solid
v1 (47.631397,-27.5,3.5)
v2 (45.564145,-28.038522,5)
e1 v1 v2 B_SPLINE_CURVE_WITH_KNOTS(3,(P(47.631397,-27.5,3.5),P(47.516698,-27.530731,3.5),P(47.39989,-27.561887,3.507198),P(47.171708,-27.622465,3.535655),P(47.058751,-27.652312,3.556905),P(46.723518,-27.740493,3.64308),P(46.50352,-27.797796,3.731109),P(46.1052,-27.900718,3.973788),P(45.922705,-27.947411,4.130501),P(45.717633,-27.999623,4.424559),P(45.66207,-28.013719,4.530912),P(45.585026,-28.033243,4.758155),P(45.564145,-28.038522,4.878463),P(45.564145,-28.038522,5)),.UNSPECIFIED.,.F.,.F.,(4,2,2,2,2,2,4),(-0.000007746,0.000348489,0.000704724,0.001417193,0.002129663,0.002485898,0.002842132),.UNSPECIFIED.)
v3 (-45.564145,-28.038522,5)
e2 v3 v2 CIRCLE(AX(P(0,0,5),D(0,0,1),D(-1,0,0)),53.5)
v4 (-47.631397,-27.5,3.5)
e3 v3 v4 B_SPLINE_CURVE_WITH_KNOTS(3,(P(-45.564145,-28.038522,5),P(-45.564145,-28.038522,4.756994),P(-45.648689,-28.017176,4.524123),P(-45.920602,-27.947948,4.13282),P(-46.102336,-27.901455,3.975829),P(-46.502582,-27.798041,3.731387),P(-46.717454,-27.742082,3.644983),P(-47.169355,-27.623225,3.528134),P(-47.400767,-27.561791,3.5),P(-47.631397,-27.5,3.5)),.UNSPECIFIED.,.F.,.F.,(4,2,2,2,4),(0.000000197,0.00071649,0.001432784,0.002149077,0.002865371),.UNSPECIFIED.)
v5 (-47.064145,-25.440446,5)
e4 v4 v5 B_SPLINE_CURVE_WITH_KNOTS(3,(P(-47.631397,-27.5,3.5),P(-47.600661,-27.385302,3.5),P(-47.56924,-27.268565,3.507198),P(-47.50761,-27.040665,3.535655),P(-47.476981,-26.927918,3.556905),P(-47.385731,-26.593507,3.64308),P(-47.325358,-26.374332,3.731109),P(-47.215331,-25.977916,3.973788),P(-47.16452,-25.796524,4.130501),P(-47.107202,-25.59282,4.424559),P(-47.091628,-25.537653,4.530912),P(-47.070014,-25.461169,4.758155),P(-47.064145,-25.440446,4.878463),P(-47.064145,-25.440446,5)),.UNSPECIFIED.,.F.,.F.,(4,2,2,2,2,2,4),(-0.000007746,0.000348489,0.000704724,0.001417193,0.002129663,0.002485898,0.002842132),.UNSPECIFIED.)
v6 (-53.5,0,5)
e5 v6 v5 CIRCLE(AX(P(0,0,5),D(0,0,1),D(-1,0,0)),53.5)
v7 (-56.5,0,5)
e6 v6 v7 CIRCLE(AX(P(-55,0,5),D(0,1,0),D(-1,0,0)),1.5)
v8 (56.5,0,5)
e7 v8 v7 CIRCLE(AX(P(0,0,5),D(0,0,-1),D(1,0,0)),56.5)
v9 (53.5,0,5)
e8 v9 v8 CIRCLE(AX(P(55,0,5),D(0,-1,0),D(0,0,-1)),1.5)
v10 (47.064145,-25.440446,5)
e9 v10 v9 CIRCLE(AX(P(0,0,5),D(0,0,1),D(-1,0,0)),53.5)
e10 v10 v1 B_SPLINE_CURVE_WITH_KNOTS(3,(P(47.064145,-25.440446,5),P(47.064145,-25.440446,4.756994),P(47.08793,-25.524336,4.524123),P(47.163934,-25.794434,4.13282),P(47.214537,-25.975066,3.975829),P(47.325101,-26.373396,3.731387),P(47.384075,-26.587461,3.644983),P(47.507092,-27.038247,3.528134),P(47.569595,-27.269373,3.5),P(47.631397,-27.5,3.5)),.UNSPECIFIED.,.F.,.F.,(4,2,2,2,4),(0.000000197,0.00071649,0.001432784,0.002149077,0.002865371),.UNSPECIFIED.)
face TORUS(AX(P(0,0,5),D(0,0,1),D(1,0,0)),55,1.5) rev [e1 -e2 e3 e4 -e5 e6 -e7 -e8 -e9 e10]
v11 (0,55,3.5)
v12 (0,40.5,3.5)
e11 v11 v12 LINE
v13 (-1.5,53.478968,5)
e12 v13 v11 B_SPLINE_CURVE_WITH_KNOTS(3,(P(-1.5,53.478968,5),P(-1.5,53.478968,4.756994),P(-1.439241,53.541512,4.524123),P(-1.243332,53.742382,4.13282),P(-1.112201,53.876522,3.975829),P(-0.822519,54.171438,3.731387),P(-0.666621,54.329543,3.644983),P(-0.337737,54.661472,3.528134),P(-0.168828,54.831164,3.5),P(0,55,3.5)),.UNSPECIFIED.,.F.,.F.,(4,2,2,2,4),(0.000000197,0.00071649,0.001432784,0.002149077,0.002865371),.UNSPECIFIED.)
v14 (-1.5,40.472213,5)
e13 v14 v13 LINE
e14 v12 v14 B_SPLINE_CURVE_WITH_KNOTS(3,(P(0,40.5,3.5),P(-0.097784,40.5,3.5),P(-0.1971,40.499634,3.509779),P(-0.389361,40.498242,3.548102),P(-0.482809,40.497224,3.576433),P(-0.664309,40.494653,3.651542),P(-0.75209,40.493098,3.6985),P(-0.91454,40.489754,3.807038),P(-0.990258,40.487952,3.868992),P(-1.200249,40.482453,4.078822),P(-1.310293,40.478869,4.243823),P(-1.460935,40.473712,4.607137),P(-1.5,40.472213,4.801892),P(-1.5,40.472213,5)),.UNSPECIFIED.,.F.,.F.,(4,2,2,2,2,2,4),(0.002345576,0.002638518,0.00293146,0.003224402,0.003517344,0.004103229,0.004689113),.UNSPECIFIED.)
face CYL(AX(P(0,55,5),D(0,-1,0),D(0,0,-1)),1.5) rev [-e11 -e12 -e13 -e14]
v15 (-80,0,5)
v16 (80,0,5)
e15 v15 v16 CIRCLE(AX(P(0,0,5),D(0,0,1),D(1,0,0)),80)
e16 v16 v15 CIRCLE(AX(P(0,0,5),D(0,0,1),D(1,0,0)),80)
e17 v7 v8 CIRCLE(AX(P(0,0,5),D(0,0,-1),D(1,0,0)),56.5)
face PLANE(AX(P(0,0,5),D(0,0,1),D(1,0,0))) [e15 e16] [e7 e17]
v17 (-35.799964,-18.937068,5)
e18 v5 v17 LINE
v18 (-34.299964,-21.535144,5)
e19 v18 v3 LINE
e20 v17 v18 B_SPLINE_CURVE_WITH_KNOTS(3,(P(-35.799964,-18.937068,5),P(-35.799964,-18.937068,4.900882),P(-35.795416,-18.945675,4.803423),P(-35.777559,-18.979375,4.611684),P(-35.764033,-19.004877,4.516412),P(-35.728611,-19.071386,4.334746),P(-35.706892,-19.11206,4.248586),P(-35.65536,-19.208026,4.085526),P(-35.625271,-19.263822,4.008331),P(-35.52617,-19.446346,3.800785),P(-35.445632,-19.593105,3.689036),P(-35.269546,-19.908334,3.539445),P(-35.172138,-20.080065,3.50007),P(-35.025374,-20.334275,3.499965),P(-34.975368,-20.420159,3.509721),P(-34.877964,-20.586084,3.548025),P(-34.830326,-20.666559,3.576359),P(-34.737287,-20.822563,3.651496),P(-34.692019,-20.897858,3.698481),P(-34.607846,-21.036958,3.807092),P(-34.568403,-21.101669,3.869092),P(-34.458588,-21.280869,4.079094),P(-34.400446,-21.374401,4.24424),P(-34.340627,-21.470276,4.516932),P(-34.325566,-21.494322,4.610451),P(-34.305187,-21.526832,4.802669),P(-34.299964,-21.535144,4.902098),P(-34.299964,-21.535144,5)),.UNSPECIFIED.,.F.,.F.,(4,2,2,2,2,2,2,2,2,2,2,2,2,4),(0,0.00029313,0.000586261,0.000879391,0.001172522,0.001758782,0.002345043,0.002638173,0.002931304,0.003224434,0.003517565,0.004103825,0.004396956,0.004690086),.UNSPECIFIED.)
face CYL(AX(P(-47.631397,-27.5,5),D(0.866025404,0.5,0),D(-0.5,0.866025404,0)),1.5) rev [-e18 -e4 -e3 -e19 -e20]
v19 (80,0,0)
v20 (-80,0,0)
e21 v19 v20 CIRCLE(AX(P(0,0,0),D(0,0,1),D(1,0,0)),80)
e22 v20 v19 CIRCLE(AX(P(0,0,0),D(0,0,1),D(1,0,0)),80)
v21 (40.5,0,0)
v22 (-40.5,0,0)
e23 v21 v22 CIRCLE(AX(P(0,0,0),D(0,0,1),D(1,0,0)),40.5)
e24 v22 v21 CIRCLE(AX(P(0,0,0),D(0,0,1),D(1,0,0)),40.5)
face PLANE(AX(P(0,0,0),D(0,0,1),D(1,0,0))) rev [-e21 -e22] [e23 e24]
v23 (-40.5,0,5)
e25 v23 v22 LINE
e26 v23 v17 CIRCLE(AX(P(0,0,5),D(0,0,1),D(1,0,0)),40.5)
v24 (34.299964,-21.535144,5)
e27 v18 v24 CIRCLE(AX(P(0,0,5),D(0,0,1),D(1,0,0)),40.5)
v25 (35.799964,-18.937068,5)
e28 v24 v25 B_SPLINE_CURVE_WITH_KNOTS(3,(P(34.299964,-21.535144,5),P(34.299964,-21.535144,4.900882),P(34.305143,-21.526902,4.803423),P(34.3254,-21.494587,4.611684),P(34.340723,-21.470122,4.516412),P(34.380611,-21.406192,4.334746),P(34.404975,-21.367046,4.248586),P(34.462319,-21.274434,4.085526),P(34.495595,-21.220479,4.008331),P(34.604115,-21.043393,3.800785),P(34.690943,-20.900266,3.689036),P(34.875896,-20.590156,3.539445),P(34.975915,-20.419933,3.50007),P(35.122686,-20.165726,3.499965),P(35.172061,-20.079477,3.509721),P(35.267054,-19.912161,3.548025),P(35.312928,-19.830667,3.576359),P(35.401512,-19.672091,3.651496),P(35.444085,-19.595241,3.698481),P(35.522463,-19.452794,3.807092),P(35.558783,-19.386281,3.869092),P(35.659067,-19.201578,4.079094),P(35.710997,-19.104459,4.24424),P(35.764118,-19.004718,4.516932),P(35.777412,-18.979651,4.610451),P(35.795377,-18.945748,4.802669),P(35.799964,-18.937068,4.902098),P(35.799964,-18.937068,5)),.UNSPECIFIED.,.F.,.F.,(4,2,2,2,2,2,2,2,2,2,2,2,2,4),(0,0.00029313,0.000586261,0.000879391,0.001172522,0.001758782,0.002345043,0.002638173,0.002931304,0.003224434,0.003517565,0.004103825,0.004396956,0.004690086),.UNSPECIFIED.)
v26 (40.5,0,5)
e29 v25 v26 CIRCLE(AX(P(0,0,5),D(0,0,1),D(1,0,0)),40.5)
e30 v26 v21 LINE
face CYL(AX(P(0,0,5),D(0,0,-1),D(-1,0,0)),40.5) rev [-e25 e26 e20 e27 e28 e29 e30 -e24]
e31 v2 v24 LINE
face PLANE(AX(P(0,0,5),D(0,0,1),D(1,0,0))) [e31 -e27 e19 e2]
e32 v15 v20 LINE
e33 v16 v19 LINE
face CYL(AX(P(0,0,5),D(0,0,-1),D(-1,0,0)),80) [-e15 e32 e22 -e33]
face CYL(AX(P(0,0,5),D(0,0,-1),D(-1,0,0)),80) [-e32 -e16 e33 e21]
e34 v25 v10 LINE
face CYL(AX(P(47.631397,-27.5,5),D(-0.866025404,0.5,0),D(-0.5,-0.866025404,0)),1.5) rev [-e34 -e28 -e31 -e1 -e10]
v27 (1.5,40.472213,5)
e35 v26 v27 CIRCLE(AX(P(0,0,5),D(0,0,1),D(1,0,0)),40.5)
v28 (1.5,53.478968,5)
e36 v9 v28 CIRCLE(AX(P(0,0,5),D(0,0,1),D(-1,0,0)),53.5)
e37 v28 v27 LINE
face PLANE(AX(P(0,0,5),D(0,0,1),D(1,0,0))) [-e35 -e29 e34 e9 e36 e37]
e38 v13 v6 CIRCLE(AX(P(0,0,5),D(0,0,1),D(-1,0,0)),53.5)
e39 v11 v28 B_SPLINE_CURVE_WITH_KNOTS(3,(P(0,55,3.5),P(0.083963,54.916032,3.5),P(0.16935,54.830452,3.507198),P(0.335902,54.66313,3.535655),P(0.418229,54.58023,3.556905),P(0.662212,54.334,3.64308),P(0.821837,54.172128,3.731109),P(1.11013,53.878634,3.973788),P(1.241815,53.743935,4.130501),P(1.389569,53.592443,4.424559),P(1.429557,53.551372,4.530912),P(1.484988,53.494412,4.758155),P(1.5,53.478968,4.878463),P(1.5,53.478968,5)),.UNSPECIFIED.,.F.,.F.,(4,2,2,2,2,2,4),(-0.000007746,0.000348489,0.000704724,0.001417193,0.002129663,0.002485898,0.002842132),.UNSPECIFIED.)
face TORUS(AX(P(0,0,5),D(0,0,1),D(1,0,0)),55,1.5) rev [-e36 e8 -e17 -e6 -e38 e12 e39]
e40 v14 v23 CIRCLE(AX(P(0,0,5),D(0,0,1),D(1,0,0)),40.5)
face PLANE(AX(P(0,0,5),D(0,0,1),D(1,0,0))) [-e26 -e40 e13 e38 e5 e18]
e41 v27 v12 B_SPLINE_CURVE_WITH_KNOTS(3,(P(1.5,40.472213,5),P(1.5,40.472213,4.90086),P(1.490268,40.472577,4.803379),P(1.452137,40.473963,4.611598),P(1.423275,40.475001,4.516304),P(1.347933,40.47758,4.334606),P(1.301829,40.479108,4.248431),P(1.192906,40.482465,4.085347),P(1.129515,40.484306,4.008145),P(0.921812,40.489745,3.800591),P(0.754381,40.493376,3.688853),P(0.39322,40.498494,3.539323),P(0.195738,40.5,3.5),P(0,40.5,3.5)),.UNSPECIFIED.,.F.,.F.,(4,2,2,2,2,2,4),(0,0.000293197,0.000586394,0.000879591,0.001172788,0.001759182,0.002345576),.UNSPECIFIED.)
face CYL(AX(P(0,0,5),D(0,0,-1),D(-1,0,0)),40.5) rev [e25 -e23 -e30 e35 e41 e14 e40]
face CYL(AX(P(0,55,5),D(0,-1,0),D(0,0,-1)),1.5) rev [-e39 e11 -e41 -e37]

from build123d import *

# Parameters (mm, degrees)
SKETCH_1_R               = 80
SKETCH_1_R_2             = 40.5
EXTRUDE_1_DEPTH          = 5
SKETCH_3_R               = 1.5
SKETCH_5_R               = 1.5
CUT_EXTRUDE_2_DEPTH      = 55
PATTERN_CIRCULAR_1_COUNT = 3


with BuildPart() as part:
    # 草图1 → 凸台-拉伸1 (new body)
    with BuildSketch(Plane.XY):
        Circle(SKETCH_1_R)
        Circle(SKETCH_1_R_2, mode=Mode.SUBTRACT)
    extrude(amount=EXTRUDE_1_DEPTH)

    # 切除-扫描1: sweep along a path in 草图2
    with BuildLine(Plane.XY.offset(5)) as sweep_1_path:
        CenterArc((0, 0), 55, 0, 360)
    # 草图3 → 切除-扫描1 (sweep, cut)
    with BuildSketch(Plane(origin=(0, 0, 0), x_dir=(0, 0, -1), z_dir=(1, 0, 0))):
        with Locations((-5, 55)):
            Circle(SKETCH_3_R)
    sweep(path=sweep_1_path.line, mode=Mode.SUBTRACT)

    # 草图5 → 切除-拉伸2 (cut)
    with BuildSketch(Plane(origin=(0, 0, 0), x_dir=(1, 0, 0), z_dir=(0, 1, 0))):
        with Locations((0, -5)):
            Circle(SKETCH_5_R)
    cut_extrude_2 = extrude(amount=CUT_EXTRUDE_2_DEPTH, mode=Mode.SUBTRACT)

    # 阵列(圆周)1: 切除-拉伸2 ×3 about axis
    pattern_circular_1_axis = Axis((0, 0, 5), (0, 0, -1))
    for i in range(1, PATTERN_CIRCULAR_1_COUNT):
        add(cut_extrude_2.rotate(pattern_circular_1_axis, i * 360 / PATTERN_CIRCULAR_1_COUNT), mode=Mode.SUBTRACT)


solid = part.part
